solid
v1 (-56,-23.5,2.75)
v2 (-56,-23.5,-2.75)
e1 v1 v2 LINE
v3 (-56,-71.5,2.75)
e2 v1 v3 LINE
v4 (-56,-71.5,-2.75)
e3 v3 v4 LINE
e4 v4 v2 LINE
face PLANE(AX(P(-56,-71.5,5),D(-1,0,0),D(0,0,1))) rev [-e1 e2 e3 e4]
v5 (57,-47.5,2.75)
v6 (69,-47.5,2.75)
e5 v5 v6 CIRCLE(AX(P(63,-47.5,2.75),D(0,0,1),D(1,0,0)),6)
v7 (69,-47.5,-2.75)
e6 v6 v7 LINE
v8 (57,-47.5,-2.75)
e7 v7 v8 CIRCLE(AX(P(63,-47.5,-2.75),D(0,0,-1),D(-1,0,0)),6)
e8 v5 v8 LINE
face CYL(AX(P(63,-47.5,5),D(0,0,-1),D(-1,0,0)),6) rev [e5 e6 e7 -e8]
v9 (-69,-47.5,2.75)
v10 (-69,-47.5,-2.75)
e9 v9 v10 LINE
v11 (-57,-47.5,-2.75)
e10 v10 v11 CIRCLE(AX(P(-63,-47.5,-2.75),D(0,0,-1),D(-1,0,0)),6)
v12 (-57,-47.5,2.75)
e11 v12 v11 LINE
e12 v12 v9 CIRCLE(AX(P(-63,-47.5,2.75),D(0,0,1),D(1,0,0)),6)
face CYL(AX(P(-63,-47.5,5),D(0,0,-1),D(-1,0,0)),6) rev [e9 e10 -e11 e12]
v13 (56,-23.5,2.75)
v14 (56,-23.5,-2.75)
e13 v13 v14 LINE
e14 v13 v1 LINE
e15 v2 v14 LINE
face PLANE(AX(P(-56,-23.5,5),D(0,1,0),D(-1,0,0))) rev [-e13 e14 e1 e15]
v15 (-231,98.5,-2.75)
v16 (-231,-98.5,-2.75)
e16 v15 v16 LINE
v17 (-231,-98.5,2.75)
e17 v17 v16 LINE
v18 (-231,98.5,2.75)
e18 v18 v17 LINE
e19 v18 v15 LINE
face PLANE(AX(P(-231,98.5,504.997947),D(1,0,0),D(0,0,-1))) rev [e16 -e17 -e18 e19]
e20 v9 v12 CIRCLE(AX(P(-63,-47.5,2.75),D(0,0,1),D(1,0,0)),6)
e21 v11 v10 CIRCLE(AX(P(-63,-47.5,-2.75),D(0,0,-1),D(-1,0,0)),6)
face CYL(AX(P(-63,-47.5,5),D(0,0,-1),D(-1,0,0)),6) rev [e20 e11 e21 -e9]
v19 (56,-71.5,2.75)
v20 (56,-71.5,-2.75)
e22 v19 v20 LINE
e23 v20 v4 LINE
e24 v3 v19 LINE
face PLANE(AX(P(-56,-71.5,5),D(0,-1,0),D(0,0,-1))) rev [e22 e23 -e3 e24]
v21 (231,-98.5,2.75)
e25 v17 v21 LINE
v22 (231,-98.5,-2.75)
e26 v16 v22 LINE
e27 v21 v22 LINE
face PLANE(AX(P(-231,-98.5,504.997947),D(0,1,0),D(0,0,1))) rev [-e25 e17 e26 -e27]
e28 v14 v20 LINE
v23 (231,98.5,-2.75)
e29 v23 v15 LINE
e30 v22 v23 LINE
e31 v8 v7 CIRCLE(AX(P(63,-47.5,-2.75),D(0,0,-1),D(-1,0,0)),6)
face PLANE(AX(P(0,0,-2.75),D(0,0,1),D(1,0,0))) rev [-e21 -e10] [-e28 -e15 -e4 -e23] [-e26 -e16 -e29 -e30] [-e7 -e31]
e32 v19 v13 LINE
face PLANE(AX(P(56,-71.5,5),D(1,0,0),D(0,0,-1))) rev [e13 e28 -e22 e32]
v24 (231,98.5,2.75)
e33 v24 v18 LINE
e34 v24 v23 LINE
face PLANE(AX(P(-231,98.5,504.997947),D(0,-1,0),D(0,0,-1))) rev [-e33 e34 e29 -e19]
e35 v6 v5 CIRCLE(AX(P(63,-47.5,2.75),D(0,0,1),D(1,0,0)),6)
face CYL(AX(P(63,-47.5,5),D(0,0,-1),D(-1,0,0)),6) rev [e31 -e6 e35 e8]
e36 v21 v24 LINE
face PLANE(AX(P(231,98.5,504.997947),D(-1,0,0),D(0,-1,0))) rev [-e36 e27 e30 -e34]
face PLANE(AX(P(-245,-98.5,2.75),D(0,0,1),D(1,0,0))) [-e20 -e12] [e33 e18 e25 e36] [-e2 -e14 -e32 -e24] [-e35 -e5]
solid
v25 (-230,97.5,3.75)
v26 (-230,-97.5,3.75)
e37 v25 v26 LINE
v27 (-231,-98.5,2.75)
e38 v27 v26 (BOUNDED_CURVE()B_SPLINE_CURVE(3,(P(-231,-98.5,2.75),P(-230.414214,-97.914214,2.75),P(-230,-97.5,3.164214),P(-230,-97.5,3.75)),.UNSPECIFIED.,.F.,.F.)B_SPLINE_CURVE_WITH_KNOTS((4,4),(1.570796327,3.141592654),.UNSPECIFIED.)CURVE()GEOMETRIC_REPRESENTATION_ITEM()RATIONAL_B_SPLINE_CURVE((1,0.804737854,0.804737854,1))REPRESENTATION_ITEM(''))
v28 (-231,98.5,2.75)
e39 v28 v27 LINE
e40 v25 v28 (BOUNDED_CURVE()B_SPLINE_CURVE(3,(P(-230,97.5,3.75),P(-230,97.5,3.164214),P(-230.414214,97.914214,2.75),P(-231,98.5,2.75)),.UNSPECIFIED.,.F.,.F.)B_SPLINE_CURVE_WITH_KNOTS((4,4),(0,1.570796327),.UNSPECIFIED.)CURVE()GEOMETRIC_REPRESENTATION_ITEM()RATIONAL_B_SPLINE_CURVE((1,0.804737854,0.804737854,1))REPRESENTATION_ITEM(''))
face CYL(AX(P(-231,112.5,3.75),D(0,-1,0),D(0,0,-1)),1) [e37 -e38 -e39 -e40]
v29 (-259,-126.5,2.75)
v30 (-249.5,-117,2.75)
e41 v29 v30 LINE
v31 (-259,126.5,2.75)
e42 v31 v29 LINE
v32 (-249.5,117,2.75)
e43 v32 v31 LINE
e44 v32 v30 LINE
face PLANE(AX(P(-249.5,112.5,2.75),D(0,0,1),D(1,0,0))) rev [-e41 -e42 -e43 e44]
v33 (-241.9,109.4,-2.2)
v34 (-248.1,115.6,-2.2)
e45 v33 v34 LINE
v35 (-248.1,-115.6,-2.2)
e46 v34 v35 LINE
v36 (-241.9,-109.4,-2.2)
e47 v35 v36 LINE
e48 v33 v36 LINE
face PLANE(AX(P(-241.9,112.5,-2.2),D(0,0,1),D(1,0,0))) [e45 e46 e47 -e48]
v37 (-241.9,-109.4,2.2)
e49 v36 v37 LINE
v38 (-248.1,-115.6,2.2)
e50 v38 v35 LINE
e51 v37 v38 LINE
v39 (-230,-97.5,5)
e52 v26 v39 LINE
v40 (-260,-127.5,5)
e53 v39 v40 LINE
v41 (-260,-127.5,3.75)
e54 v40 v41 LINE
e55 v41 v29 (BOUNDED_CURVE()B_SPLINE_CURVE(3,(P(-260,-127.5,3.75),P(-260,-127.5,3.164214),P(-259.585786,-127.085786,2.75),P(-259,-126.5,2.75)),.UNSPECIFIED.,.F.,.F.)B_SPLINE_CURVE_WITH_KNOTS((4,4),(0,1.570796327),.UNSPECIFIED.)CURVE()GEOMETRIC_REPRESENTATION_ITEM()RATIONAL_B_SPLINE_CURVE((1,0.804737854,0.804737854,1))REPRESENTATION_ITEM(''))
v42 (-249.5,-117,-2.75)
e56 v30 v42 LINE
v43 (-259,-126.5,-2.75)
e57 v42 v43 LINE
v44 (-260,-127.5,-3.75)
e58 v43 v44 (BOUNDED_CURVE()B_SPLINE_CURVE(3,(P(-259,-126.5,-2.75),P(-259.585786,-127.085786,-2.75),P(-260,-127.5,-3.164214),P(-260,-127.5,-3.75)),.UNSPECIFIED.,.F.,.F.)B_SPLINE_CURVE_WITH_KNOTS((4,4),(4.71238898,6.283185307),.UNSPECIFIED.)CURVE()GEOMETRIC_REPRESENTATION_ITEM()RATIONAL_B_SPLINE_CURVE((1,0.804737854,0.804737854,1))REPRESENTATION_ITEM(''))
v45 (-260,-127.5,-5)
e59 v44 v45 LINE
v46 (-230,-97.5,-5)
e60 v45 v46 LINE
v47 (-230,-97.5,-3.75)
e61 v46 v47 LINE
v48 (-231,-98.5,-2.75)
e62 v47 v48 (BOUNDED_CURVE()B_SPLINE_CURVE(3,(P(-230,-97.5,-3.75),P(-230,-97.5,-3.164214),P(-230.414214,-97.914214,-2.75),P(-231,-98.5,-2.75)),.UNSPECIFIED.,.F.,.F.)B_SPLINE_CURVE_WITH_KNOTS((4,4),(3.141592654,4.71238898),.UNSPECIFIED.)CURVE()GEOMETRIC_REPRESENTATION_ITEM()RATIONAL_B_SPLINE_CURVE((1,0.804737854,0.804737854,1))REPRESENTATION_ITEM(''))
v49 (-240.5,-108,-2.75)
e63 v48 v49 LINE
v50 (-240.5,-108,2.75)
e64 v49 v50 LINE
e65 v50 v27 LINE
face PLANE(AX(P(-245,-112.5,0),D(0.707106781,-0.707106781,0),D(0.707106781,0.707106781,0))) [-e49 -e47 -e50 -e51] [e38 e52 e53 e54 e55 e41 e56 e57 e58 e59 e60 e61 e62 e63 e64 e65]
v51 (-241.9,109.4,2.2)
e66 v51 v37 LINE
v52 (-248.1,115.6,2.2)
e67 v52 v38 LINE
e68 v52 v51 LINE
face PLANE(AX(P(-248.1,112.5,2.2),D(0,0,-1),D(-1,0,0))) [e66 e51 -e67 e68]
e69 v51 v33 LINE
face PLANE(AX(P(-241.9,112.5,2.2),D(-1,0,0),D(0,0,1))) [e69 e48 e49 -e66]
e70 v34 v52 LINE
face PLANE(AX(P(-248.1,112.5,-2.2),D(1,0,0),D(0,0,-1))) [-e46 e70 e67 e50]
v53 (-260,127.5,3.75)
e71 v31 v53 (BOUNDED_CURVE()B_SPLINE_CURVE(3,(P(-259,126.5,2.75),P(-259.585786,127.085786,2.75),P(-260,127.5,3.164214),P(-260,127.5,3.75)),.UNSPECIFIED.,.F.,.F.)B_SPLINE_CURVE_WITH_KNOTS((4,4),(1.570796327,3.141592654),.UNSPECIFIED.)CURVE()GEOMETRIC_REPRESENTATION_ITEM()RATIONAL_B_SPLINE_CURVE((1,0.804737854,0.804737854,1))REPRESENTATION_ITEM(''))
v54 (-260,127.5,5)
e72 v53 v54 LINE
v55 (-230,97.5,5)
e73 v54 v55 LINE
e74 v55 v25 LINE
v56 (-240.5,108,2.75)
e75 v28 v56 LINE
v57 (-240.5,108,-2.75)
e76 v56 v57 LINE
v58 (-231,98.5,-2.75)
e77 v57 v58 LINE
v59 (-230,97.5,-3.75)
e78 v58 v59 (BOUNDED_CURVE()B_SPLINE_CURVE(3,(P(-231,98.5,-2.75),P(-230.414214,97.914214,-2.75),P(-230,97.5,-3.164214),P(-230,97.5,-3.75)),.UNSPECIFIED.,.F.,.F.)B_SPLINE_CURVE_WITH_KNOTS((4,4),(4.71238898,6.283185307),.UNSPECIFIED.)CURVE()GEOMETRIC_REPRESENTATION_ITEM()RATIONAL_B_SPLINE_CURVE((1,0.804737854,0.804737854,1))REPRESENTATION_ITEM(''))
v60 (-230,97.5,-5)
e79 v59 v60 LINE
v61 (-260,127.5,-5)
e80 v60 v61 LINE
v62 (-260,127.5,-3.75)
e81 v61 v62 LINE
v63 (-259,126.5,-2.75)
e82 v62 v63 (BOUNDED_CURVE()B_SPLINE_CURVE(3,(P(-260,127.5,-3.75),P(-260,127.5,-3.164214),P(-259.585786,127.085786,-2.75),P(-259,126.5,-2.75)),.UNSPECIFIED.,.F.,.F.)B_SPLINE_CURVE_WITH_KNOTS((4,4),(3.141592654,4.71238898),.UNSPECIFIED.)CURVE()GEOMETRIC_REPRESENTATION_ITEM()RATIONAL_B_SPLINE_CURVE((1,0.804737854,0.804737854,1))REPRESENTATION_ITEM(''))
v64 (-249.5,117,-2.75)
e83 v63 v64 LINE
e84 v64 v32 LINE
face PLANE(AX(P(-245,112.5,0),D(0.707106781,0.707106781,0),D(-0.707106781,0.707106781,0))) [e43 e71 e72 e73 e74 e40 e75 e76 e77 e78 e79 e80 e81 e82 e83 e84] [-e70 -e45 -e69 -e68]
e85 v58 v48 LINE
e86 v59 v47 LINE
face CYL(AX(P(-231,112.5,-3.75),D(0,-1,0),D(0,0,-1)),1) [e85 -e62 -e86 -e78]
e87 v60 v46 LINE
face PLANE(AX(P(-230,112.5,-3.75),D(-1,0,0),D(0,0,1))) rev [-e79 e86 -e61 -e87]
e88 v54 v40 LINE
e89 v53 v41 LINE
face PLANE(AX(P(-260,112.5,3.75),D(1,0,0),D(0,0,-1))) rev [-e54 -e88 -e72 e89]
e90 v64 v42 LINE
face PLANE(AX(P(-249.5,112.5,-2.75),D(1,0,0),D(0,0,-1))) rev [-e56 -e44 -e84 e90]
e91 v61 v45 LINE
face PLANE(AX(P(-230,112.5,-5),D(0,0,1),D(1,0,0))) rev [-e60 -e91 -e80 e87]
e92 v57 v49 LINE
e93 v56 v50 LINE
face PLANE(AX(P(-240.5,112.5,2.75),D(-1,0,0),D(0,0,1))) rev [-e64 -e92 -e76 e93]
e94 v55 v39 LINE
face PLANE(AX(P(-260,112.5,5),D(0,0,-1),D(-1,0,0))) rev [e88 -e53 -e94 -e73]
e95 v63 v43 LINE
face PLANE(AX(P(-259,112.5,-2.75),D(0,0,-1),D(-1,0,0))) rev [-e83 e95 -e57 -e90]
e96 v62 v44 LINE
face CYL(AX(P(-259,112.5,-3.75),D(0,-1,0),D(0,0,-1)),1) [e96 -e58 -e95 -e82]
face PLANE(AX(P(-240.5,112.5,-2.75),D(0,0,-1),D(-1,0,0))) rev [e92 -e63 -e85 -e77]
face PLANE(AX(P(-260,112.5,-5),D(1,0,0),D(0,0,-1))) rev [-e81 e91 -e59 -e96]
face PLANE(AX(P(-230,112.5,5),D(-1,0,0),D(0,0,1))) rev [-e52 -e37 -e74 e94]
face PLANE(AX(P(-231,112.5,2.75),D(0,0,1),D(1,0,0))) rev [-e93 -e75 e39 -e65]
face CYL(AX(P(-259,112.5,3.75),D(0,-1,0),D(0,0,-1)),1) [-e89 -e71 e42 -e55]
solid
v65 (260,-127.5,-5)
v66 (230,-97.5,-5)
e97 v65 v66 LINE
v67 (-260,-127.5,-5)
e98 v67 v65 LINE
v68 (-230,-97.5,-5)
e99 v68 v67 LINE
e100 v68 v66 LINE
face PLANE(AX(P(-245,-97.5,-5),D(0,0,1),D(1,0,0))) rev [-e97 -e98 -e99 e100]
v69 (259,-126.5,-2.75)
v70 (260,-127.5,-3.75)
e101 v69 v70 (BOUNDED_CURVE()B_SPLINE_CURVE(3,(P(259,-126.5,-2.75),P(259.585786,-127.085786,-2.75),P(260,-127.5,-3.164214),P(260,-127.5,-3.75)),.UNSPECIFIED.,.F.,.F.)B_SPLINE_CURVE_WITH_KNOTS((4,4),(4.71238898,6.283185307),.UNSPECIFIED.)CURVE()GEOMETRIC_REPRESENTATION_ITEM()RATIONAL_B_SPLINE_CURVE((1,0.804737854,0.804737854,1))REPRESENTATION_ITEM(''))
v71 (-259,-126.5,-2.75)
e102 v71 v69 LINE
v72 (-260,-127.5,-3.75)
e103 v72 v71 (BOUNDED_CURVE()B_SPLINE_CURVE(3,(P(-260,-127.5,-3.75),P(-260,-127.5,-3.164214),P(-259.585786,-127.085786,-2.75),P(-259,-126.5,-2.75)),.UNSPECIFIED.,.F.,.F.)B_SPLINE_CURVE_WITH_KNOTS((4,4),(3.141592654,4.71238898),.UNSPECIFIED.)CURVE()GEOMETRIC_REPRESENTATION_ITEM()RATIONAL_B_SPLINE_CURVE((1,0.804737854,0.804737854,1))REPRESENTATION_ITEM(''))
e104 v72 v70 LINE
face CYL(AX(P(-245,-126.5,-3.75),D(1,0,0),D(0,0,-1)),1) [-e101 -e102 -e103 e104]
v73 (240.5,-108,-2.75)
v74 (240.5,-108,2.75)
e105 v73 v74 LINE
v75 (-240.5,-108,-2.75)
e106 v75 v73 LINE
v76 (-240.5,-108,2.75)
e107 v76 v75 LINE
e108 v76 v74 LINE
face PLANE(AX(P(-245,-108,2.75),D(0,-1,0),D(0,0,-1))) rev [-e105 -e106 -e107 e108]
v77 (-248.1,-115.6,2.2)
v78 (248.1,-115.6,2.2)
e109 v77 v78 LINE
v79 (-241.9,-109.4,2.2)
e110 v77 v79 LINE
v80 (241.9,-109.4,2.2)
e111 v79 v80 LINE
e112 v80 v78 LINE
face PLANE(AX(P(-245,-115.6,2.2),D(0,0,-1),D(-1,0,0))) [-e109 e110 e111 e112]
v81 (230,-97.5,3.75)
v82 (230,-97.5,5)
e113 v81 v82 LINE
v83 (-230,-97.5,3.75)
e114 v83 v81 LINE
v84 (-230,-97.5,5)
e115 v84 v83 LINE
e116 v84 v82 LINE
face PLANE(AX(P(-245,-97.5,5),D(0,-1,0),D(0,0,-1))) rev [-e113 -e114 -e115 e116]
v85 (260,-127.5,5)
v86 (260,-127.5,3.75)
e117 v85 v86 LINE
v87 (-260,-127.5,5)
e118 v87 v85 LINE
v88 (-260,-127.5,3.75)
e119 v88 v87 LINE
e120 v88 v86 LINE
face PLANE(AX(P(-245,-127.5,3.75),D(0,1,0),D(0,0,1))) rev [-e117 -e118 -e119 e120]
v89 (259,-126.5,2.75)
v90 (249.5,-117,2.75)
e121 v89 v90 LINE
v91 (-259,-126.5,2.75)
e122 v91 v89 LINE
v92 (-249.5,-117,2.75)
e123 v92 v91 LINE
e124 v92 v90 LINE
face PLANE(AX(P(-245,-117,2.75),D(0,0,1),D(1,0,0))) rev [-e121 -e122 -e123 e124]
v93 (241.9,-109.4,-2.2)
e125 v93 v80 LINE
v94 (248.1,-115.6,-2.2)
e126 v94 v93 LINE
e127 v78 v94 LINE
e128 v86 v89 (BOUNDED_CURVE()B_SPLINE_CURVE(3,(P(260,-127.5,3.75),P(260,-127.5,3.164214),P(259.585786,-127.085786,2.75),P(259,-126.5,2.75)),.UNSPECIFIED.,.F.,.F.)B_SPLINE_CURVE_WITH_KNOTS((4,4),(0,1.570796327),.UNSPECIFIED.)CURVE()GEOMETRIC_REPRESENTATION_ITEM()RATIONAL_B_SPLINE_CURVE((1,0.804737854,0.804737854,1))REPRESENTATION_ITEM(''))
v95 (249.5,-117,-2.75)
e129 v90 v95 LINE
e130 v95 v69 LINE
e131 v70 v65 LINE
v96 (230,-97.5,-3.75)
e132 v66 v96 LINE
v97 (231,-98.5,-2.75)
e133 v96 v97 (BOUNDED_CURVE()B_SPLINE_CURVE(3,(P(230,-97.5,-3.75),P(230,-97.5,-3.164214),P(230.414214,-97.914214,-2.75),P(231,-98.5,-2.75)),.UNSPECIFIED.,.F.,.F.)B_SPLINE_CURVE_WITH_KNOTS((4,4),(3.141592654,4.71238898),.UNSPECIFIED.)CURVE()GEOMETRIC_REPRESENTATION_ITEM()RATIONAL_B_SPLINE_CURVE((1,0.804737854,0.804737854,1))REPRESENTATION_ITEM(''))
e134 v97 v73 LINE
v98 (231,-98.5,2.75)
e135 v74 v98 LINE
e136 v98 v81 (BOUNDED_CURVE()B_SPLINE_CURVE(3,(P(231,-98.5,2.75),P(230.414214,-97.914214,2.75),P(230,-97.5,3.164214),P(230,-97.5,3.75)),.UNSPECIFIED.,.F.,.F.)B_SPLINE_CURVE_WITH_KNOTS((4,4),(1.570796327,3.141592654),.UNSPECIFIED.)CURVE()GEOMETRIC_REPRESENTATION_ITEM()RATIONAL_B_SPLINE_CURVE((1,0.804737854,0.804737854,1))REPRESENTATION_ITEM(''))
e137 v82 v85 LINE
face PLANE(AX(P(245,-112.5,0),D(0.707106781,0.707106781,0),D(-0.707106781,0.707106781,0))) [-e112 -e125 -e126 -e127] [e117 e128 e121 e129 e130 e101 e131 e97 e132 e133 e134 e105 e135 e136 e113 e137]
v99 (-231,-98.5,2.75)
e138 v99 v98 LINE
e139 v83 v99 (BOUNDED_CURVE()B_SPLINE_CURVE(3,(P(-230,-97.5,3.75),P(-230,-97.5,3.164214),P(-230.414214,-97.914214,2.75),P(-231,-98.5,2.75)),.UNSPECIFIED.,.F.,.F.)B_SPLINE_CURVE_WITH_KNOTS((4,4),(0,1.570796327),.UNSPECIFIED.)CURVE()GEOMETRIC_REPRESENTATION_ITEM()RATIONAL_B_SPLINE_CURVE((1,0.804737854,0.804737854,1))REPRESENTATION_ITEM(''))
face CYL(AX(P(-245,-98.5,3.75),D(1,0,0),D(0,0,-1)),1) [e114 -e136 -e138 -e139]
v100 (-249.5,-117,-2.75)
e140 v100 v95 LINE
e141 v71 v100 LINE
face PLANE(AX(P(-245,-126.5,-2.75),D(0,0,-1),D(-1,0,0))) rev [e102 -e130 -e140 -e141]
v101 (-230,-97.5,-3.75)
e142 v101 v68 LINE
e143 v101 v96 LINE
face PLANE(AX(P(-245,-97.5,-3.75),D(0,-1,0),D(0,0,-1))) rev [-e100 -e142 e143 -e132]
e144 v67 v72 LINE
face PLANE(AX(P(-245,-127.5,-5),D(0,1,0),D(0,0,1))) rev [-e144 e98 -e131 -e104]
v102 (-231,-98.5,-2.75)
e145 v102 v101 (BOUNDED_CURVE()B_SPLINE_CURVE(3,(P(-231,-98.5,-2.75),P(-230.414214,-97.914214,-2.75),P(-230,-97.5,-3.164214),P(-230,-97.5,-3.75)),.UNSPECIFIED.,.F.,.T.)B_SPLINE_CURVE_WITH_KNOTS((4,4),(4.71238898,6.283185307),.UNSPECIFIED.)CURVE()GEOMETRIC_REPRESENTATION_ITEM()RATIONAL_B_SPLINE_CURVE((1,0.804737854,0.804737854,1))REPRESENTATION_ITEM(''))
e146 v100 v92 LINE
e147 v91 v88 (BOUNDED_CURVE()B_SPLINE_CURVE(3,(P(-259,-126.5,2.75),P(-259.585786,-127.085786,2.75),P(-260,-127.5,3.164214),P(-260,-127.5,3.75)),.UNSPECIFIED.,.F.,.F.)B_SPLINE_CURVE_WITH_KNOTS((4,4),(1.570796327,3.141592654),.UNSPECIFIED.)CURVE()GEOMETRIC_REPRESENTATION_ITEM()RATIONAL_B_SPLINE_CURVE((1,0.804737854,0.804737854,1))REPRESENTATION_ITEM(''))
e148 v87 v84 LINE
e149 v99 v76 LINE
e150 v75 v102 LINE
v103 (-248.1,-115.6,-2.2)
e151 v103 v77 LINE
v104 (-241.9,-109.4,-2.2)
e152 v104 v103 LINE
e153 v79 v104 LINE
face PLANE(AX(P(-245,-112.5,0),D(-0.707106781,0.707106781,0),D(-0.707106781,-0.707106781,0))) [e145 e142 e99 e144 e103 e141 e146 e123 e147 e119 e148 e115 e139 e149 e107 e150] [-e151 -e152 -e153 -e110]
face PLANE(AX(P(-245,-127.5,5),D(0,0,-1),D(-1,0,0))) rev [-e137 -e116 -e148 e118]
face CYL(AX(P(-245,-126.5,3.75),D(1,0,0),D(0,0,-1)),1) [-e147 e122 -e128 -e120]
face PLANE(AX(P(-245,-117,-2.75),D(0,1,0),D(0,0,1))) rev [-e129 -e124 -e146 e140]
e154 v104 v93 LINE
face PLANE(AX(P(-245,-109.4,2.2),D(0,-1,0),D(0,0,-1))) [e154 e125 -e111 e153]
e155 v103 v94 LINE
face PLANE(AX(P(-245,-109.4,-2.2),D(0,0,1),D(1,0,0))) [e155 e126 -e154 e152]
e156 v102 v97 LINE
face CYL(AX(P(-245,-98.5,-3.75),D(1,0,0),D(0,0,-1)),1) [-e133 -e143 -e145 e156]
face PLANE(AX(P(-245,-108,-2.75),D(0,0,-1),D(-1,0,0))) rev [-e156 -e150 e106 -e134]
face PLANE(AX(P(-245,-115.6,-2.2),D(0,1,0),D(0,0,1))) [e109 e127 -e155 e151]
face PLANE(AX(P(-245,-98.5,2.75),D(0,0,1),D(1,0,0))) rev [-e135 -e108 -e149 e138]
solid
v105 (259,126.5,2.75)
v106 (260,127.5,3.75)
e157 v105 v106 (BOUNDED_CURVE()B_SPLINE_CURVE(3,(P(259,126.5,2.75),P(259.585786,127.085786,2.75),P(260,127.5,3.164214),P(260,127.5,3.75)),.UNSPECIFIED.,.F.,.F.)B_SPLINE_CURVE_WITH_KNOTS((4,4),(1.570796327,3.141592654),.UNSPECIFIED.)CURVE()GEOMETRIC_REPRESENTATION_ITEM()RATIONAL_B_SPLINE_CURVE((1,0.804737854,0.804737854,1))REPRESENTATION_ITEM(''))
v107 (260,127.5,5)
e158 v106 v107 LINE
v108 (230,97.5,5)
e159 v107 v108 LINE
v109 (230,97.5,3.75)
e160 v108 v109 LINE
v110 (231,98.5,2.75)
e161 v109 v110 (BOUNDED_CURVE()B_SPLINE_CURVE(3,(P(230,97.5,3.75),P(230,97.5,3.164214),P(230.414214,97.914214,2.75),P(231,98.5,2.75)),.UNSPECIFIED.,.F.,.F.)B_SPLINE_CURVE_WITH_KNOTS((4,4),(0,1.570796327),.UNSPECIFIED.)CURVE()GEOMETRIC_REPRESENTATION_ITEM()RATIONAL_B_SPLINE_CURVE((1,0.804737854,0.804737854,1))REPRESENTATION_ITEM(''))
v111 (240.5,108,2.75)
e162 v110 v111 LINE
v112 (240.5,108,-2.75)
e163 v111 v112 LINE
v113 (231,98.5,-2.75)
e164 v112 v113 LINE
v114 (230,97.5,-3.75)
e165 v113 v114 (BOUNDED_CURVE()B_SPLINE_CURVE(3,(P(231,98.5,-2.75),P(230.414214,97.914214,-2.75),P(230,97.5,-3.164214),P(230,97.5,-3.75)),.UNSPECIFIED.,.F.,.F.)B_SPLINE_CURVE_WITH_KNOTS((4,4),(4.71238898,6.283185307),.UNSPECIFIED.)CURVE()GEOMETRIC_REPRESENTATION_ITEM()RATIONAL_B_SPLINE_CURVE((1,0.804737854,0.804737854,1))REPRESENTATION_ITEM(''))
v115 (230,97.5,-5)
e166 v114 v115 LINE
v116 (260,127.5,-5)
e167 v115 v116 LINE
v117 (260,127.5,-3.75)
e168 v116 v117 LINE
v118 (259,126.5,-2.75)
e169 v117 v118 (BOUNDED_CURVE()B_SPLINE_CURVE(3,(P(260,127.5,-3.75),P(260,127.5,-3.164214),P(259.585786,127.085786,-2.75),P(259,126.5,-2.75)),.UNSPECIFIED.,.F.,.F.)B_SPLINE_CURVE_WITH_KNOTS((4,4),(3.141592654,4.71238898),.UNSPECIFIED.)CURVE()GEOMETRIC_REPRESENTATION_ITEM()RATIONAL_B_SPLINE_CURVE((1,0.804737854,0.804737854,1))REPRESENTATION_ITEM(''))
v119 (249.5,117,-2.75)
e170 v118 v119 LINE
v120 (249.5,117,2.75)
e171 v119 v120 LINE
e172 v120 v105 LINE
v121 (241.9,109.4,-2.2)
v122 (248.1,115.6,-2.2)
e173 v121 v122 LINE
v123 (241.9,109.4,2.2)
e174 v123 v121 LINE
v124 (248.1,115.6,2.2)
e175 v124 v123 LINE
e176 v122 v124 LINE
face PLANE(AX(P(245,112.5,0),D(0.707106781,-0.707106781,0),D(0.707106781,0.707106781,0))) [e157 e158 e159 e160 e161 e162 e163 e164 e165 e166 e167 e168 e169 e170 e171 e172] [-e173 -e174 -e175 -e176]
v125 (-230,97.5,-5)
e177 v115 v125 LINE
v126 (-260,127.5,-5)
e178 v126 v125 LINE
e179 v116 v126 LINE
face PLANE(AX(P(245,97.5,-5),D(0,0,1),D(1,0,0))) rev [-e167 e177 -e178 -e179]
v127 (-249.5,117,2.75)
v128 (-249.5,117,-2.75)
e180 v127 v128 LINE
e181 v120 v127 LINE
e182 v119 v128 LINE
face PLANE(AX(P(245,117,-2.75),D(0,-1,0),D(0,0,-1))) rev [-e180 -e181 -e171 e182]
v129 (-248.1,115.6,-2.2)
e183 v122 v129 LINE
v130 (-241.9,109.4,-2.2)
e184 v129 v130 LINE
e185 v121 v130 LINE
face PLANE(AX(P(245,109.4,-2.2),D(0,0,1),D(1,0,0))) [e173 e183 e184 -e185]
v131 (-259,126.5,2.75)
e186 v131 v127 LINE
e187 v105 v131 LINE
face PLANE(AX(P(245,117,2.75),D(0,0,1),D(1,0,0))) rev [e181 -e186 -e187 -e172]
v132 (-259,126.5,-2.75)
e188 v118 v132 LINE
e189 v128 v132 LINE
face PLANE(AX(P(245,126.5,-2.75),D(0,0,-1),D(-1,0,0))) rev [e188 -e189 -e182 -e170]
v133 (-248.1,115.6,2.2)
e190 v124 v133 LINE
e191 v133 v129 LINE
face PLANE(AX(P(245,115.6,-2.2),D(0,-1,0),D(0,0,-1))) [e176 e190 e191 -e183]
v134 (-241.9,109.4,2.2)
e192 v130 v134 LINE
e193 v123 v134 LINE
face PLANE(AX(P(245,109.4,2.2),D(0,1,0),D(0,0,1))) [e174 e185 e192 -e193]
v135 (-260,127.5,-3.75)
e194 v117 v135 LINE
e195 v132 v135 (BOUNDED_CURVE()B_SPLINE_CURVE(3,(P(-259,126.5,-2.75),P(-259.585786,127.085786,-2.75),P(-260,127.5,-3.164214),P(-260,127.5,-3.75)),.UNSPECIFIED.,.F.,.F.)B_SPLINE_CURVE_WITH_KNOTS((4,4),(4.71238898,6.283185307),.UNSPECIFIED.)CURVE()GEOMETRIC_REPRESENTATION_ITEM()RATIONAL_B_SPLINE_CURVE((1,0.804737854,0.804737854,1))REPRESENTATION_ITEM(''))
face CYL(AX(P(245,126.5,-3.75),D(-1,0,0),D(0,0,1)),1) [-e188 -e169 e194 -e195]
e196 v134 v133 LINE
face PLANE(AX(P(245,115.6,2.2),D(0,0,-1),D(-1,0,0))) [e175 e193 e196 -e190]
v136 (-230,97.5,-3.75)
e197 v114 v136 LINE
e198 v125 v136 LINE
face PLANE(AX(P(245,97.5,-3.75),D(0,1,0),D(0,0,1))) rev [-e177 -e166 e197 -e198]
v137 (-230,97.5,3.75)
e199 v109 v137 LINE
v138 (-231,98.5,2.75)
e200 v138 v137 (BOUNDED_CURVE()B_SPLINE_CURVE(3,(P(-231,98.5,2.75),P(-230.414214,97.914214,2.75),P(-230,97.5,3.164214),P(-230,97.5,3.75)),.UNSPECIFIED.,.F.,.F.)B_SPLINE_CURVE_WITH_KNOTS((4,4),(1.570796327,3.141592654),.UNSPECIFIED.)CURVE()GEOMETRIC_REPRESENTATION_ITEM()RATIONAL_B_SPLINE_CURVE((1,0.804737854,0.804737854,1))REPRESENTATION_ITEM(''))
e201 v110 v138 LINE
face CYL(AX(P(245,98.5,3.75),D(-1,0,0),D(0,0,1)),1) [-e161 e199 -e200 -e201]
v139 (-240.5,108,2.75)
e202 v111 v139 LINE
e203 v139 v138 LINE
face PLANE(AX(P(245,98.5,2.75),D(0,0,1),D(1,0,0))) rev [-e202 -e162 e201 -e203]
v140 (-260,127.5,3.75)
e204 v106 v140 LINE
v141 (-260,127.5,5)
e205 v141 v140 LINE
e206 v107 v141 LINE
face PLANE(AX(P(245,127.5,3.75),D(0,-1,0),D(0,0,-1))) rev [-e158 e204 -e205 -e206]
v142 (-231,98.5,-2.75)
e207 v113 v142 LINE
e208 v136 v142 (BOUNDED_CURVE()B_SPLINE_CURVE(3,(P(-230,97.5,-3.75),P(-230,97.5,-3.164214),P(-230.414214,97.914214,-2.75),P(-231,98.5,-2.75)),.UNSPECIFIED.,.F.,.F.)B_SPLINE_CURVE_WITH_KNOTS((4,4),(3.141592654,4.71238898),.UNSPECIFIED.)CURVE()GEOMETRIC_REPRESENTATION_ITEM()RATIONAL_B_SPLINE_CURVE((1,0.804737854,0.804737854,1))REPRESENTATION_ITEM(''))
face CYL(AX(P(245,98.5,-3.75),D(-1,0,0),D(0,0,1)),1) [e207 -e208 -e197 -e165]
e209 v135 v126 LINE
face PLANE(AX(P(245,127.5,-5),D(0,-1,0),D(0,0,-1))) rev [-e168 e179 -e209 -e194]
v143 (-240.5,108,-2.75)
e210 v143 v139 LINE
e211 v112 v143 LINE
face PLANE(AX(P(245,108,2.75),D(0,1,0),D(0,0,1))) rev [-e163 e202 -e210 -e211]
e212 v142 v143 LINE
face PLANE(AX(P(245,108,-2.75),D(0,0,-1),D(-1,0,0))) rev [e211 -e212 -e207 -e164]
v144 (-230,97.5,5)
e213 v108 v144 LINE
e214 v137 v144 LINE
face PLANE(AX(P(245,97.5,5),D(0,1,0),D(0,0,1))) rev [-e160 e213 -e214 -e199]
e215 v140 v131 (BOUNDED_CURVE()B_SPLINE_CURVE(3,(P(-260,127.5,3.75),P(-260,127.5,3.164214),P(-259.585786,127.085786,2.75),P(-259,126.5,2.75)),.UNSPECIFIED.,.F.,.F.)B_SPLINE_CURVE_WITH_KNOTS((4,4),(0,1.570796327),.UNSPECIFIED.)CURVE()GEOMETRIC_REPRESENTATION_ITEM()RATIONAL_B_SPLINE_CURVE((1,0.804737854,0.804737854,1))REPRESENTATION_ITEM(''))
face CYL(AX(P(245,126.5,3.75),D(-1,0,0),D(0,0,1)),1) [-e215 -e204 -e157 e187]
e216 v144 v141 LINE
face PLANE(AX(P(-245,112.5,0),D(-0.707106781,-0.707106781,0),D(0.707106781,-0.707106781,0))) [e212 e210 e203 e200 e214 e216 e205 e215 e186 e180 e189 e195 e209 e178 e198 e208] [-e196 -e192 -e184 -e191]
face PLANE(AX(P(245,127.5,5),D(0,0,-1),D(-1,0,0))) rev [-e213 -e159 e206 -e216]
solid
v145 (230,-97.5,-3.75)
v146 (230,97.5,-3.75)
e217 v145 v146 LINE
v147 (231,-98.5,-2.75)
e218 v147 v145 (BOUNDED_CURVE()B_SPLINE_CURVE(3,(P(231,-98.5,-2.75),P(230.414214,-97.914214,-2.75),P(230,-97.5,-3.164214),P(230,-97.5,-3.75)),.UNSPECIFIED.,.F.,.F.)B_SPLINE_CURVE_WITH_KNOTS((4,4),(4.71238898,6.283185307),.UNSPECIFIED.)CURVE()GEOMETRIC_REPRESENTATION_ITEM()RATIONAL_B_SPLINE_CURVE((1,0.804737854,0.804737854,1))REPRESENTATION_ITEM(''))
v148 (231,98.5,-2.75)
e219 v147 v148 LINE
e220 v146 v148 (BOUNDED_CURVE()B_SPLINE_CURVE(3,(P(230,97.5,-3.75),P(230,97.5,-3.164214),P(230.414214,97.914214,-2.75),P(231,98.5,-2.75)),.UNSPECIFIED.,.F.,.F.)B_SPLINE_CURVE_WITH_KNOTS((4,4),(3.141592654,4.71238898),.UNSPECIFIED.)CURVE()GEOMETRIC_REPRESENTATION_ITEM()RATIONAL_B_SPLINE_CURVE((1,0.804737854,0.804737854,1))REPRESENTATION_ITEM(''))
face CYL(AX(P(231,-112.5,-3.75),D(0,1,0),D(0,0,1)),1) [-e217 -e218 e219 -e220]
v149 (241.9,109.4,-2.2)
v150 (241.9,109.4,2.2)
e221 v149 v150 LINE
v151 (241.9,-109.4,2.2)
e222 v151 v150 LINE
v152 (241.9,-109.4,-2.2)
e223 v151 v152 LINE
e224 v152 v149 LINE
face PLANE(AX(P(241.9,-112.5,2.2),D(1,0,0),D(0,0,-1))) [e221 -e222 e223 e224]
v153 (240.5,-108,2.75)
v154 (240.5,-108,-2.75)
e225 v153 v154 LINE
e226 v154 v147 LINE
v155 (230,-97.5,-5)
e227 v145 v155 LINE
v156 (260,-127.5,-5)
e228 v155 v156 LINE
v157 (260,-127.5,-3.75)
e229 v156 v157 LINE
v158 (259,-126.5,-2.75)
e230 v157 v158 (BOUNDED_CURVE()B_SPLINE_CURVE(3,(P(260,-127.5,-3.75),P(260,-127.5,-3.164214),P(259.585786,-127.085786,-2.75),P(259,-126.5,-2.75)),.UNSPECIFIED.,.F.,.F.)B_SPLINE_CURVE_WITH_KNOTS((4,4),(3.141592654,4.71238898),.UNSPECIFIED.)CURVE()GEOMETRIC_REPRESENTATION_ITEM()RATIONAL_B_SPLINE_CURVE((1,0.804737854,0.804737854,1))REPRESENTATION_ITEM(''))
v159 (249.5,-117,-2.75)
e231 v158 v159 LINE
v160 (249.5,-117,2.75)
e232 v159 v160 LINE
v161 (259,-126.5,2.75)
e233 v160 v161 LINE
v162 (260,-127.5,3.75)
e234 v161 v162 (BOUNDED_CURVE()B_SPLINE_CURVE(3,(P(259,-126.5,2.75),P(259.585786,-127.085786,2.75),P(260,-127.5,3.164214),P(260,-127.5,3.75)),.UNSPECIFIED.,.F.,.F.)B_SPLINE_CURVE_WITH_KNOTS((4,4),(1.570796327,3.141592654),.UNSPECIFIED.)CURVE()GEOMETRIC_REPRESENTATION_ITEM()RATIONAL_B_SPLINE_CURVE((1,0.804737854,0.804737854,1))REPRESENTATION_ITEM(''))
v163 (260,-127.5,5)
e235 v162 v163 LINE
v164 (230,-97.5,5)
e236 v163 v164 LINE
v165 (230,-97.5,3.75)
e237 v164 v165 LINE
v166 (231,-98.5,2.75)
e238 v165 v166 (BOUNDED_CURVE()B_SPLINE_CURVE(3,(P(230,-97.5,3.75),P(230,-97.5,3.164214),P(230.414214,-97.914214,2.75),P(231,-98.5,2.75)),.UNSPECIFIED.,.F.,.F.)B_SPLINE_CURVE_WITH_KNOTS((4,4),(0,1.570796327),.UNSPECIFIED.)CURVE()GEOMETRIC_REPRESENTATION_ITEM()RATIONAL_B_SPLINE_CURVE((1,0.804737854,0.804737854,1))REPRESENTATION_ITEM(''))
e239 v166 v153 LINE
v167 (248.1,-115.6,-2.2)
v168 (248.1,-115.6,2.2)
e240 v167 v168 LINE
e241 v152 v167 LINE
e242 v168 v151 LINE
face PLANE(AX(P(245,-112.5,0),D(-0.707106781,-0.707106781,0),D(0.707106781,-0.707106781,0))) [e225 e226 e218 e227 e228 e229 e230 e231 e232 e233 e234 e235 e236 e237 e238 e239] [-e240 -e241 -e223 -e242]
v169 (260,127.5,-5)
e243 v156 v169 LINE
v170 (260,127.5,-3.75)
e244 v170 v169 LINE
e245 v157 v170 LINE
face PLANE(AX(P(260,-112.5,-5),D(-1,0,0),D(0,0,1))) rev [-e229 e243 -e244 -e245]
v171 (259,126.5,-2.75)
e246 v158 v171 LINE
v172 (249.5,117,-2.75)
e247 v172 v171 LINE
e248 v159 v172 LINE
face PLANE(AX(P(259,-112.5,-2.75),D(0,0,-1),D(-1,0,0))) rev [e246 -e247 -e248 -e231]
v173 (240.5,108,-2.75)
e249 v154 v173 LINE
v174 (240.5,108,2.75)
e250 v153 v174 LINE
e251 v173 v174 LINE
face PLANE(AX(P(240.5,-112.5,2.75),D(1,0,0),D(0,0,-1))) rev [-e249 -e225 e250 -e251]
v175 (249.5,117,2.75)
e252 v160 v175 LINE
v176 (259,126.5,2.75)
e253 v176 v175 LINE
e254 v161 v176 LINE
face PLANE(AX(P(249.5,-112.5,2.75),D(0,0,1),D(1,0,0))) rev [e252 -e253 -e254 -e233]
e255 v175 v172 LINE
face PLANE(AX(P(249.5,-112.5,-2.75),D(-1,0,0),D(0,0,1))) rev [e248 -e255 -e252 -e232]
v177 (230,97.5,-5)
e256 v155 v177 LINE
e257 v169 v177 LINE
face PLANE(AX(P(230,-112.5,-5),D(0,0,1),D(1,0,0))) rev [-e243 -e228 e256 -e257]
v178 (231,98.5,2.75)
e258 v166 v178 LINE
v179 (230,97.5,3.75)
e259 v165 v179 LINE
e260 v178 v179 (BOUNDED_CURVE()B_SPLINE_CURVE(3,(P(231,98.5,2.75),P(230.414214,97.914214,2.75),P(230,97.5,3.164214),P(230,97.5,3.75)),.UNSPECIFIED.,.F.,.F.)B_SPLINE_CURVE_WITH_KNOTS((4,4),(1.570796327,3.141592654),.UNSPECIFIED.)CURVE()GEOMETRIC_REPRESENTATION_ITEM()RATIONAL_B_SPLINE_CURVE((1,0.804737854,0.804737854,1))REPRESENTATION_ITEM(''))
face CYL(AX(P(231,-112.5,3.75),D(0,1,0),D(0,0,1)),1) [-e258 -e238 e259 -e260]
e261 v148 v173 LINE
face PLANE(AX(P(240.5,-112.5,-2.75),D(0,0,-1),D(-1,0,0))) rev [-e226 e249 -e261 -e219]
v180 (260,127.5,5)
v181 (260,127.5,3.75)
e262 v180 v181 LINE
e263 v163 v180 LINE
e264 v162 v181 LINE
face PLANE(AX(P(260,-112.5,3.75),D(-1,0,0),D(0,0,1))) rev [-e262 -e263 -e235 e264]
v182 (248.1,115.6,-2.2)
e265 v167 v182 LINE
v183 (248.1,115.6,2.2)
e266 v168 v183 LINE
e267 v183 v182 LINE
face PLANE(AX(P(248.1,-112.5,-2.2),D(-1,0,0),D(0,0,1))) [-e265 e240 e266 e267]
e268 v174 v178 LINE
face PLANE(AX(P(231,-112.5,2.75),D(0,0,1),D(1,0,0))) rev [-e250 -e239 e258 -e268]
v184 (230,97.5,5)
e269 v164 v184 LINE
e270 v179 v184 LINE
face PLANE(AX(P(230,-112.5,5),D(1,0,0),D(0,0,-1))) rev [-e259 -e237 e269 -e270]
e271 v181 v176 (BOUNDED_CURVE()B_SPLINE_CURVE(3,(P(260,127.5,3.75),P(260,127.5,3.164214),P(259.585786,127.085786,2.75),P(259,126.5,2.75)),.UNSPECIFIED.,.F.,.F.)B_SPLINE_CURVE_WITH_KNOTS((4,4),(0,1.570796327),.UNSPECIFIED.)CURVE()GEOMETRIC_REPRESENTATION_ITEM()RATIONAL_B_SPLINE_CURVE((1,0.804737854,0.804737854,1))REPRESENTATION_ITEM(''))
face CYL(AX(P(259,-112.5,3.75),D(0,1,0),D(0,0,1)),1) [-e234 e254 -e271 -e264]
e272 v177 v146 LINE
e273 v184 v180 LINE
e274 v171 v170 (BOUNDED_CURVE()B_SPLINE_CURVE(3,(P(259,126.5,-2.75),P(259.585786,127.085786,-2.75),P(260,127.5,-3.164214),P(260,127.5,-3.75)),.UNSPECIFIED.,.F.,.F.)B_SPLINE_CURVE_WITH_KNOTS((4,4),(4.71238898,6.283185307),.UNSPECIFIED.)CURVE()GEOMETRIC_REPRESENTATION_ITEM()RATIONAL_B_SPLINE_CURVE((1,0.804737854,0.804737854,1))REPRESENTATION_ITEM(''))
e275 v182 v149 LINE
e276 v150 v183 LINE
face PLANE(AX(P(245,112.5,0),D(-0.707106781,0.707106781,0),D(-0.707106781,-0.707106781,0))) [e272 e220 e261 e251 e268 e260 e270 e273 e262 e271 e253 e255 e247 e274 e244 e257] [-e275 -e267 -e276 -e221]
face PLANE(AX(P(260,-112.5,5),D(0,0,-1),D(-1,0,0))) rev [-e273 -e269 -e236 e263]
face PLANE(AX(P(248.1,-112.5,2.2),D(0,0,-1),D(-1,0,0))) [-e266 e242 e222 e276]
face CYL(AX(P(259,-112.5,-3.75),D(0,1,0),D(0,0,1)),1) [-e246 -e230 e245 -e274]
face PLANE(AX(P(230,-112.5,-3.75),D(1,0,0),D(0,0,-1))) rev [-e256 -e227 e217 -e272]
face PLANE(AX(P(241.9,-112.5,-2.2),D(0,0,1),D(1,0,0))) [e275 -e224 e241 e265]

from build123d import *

# Parameters (mm, degrees)
ALUMINIUM_PROFILE_20_X_20_X_2_1_DEPTH      = 506.811388301
ALUMINIUM_PROFILE_20_X_20_X_2_1_DEPTH_BACK = 16.811388301
SKETCH1_W                                  = 6.2
SKETCH1_H                                  = 4.4
SKETCH1_ON_SEGMENT_2_W                     = 6.2
SKETCH1_ON_SEGMENT_2_H                     = 4.4
ALUMINIUM_PROFILE_20_X_20_X_2_1_2_DEPTH    = 258.622776602
SKETCH1_ON_SEGMENT_3_W                     = 6.2
SKETCH1_ON_SEGMENT_3_H                     = 4.4
ALUMINIUM_PROFILE_20_X_20_X_2_1_3_DEPTH    = 523.622776602
SKETCH1_ON_SEGMENT_4_W                     = 6.2
SKETCH1_ON_SEGMENT_4_H                     = 4.4
ALUMINIUM_PROFILE_20_X_20_X_2_1_4_DEPTH    = 258.622776602
SKETCH3_W                                  = 462
SKETCH3_H                                  = 197
BOSS_EXTRUDE1_DEPTH                        = 5.5
SKETCH4_R                                  = 6
SKETCH4_W                                  = 112
SKETCH4_H                                  = 48
CUT_EXTRUDE1_DEPTH                         = 290.683124293


with BuildPart() as part:
    # Sketch1 → Aluminium profile 20 X 20 X 2(1) (new, two sides: drawn at the far end of the back side and taken through both)
    with BuildSketch(Plane(origin=(-245, 112.5, 0), x_dir=(0, 1, 0), z_dir=(1, 0, 0)).offset(-ALUMINIUM_PROFILE_20_X_20_X_2_1_DEPTH_BACK)):
        with BuildLine():
            Line((4.5, 2.75), (14, 2.75))
            ThreePointArc((14, 2.75), (14.707106781, 3.042893219), (15, 3.75))
            Line((15, 3.75), (15, 5))
            Line((15, 5), (-15, 5))
            Line((-15, 5), (-15, 3.75))
            ThreePointArc((-15, 3.75), (-14.707106781, 3.042893219), (-14, 2.75))
            Line((-14, 2.75), (-4.5, 2.75))
            Line((-4.5, 2.75), (-4.5, -2.75))
            Line((-4.5, -2.75), (-14, -2.75))
            ThreePointArc((-14, -2.75), (-14.707106781, -3.042893219), (-15, -3.75))
            Line((-15, -3.75), (-15, -5))
            Line((-15, -5), (15, -5))
            Line((15, -5), (15, -3.75))
            ThreePointArc((15, -3.75), (14.707106781, -3.042893219), (14, -2.75))
            Line((14, -2.75), (4.5, -2.75))
            Line((4.5, -2.75), (4.5, 2.75))
        make_face()
        Rectangle(SKETCH1_W, SKETCH1_H, mode=Mode.SUBTRACT)
    extrude(amount=ALUMINIUM_PROFILE_20_X_20_X_2_1_DEPTH + ALUMINIUM_PROFILE_20_X_20_X_2_1_DEPTH_BACK)

    # Aluminium profile 20 X 20 X 2(1) mitre 1
    split(bisect_by=Plane(origin=(-245, 112.5, 0), x_dir=(-0.707106781, 0.707106781, 0), z_dir=(0.707106781, 0.707106781, 0)), keep=Keep.TOP)

    # Aluminium profile 20 X 20 X 2(1) mitre 2
    split(bisect_by=Plane(origin=(245, 112.5, 0), x_dir=(-0.707106781, -0.707106781, 0), z_dir=(-0.707106781, 0.707106781, 0)), keep=Keep.TOP)


with BuildPart() as body_2:
    # Sketch1 on segment 2 (carried to segment 2) → Aluminium profile 20 X 20 X 2_1 2 (new body)
    with BuildSketch(Plane(origin=(245, 129.311388301, 0), x_dir=(1, 0, 0), z_dir=(0, -1, 0))):
        with BuildLine():
            Line((4.5, 2.75), (14, 2.75))
            ThreePointArc((14, 2.75), (14.707106781, 3.042893219), (15, 3.75))
            Line((15, 3.75), (15, 5))
            Line((15, 5), (-15, 5))
            Line((-15, 5), (-15, 3.75))
            ThreePointArc((-15, 3.75), (-14.707106781, 3.042893219), (-14, 2.75))
            Line((-14, 2.75), (-4.5, 2.75))
            Line((-4.5, 2.75), (-4.5, -2.75))
            Line((-4.5, -2.75), (-14, -2.75))
            ThreePointArc((-14, -2.75), (-14.707106781, -3.042893219), (-15, -3.75))
            Line((-15, -3.75), (-15, -5))
            Line((-15, -5), (15, -5))
            Line((15, -5), (15, -3.75))
            ThreePointArc((15, -3.75), (14.707106781, -3.042893219), (14, -2.75))
            Line((14, -2.75), (4.5, -2.75))
            Line((4.5, -2.75), (4.5, 2.75))
        make_face()
        Rectangle(SKETCH1_ON_SEGMENT_2_W, SKETCH1_ON_SEGMENT_2_H, mode=Mode.SUBTRACT)
    extrude(amount=ALUMINIUM_PROFILE_20_X_20_X_2_1_2_DEPTH)

    # Aluminium profile 20 X 20 X 2_1 2 mitre
    split(bisect_by=Plane(origin=(245, -112.5, 0), x_dir=(-0.707106781, 0.707106781, 0), z_dir=(0.707106781, 0.707106781, 0)), keep=Keep.TOP)

    # Aluminium profile 20 X 20 X 2_1 2 mi 2
    split(bisect_by=Plane(origin=(245, 112.5, 0), x_dir=(0.707106781, 0.707106781, 0), z_dir=(0.707106781, -0.707106781, 0)), keep=Keep.TOP)


with BuildPart() as body_3:
    # Sketch1 on segment 3 (carried to segment 3) → Aluminium profile 20 X 20 X 2_1 3 (new body)
    with BuildSketch(Plane(origin=(261.811388301, -112.5, 0), x_dir=(0, -1, 0), z_dir=(-1, 0, 0))):
        with BuildLine():
            Line((4.5, 2.75), (14, 2.75))
            ThreePointArc((14, 2.75), (14.707106781, 3.042893219), (15, 3.75))
            Line((15, 3.75), (15, 5))
            Line((15, 5), (-15, 5))
            Line((-15, 5), (-15, 3.75))
            ThreePointArc((-15, 3.75), (-14.707106781, 3.042893219), (-14, 2.75))
            Line((-14, 2.75), (-4.5, 2.75))
            Line((-4.5, 2.75), (-4.5, -2.75))
            Line((-4.5, -2.75), (-14, -2.75))
            ThreePointArc((-14, -2.75), (-14.707106781, -3.042893219), (-15, -3.75))
            Line((-15, -3.75), (-15, -5))
            Line((-15, -5), (15, -5))
            Line((15, -5), (15, -3.75))
            ThreePointArc((15, -3.75), (14.707106781, -3.042893219), (14, -2.75))
            Line((14, -2.75), (4.5, -2.75))
            Line((4.5, -2.75), (4.5, 2.75))
        make_face()
        Rectangle(SKETCH1_ON_SEGMENT_3_W, SKETCH1_ON_SEGMENT_3_H, mode=Mode.SUBTRACT)
    extrude(amount=ALUMINIUM_PROFILE_20_X_20_X_2_1_3_DEPTH)

    # Aluminium profile 20 X 20 X 2_1 3 mitre
    split(bisect_by=Plane(origin=(-245, -112.5, 0), x_dir=(0.707106781, 0.707106781, 0), z_dir=(0.707106781, -0.707106781, 0)), keep=Keep.TOP)

    # Aluminium profile 20 X 20 X 2_1 3 mi 2
    split(bisect_by=Plane(origin=(245, -112.5, 0), x_dir=(0.707106781, -0.707106781, 0), z_dir=(-0.707106781, -0.707106781, 0)), keep=Keep.TOP)


with BuildPart() as body_4:
    # Sketch1 on segment 4 (carried to segment 4) → Aluminium profile 20 X 20 X 2_1 4 (new body)
    with BuildSketch(Plane(origin=(-245, -129.311388301, 0), x_dir=(-1, 0, 0), z_dir=(0, 1, 0))):
        with BuildLine():
            Line((4.5, 2.75), (14, 2.75))
            ThreePointArc((14, 2.75), (14.707106781, 3.042893219), (15, 3.75))
            Line((15, 3.75), (15, 5))
            Line((15, 5), (-15, 5))
            Line((-15, 5), (-15, 3.75))
            ThreePointArc((-15, 3.75), (-14.707106781, 3.042893219), (-14, 2.75))
            Line((-14, 2.75), (-4.5, 2.75))
            Line((-4.5, 2.75), (-4.5, -2.75))
            Line((-4.5, -2.75), (-14, -2.75))
            ThreePointArc((-14, -2.75), (-14.707106781, -3.042893219), (-15, -3.75))
            Line((-15, -3.75), (-15, -5))
            Line((-15, -5), (15, -5))
            Line((15, -5), (15, -3.75))
            ThreePointArc((15, -3.75), (14.707106781, -3.042893219), (14, -2.75))
            Line((14, -2.75), (4.5, -2.75))
            Line((4.5, -2.75), (4.5, 2.75))
        make_face()
        Rectangle(SKETCH1_ON_SEGMENT_4_W, SKETCH1_ON_SEGMENT_4_H, mode=Mode.SUBTRACT)
    extrude(amount=ALUMINIUM_PROFILE_20_X_20_X_2_1_4_DEPTH)

    # Aluminium profile 20 X 20 X 2_1 4 mitre
    split(bisect_by=Plane(origin=(-245, -112.5, 0), x_dir=(-0.707106781, -0.707106781, 0), z_dir=(-0.707106781, 0.707106781, 0)), keep=Keep.TOP)

    # Aluminium profile 20 X 20 X 2_1 4 mi 2
    split(bisect_by=Plane(origin=(-245, 112.5, 0), x_dir=(0.707106781, -0.707106781, 0), z_dir=(-0.707106781, -0.707106781, 0)), keep=Keep.TOP)


with BuildPart() as body_5:
    # Sketch3 → Boss-Extrude1 (new body)
    with BuildSketch(Plane.XY.offset(-2.75)):
        Rectangle(SKETCH3_W, SKETCH3_H)
    extrude(amount=BOSS_EXTRUDE1_DEPTH)

    # Sketch4 → Cut-Extrude1 (cut, through all)
    with BuildSketch(Plane(origin=(0, 0, -2.75), x_dir=(-1, 0, 0), z_dir=(0, 0, -1))):
        with Locations((-63, -47.5)):
            Circle(SKETCH4_R)
        with Locations((63, -47.5)):
            Circle(SKETCH4_R)
        with Locations((0, -47.5)):
            Rectangle(SKETCH4_W, SKETCH4_H)
    extrude(amount=-CUT_EXTRUDE1_DEPTH, mode=Mode.SUBTRACT)


solid = Compound([part.part, body_2.part, body_3.part, body_4.part, body_5.part])
